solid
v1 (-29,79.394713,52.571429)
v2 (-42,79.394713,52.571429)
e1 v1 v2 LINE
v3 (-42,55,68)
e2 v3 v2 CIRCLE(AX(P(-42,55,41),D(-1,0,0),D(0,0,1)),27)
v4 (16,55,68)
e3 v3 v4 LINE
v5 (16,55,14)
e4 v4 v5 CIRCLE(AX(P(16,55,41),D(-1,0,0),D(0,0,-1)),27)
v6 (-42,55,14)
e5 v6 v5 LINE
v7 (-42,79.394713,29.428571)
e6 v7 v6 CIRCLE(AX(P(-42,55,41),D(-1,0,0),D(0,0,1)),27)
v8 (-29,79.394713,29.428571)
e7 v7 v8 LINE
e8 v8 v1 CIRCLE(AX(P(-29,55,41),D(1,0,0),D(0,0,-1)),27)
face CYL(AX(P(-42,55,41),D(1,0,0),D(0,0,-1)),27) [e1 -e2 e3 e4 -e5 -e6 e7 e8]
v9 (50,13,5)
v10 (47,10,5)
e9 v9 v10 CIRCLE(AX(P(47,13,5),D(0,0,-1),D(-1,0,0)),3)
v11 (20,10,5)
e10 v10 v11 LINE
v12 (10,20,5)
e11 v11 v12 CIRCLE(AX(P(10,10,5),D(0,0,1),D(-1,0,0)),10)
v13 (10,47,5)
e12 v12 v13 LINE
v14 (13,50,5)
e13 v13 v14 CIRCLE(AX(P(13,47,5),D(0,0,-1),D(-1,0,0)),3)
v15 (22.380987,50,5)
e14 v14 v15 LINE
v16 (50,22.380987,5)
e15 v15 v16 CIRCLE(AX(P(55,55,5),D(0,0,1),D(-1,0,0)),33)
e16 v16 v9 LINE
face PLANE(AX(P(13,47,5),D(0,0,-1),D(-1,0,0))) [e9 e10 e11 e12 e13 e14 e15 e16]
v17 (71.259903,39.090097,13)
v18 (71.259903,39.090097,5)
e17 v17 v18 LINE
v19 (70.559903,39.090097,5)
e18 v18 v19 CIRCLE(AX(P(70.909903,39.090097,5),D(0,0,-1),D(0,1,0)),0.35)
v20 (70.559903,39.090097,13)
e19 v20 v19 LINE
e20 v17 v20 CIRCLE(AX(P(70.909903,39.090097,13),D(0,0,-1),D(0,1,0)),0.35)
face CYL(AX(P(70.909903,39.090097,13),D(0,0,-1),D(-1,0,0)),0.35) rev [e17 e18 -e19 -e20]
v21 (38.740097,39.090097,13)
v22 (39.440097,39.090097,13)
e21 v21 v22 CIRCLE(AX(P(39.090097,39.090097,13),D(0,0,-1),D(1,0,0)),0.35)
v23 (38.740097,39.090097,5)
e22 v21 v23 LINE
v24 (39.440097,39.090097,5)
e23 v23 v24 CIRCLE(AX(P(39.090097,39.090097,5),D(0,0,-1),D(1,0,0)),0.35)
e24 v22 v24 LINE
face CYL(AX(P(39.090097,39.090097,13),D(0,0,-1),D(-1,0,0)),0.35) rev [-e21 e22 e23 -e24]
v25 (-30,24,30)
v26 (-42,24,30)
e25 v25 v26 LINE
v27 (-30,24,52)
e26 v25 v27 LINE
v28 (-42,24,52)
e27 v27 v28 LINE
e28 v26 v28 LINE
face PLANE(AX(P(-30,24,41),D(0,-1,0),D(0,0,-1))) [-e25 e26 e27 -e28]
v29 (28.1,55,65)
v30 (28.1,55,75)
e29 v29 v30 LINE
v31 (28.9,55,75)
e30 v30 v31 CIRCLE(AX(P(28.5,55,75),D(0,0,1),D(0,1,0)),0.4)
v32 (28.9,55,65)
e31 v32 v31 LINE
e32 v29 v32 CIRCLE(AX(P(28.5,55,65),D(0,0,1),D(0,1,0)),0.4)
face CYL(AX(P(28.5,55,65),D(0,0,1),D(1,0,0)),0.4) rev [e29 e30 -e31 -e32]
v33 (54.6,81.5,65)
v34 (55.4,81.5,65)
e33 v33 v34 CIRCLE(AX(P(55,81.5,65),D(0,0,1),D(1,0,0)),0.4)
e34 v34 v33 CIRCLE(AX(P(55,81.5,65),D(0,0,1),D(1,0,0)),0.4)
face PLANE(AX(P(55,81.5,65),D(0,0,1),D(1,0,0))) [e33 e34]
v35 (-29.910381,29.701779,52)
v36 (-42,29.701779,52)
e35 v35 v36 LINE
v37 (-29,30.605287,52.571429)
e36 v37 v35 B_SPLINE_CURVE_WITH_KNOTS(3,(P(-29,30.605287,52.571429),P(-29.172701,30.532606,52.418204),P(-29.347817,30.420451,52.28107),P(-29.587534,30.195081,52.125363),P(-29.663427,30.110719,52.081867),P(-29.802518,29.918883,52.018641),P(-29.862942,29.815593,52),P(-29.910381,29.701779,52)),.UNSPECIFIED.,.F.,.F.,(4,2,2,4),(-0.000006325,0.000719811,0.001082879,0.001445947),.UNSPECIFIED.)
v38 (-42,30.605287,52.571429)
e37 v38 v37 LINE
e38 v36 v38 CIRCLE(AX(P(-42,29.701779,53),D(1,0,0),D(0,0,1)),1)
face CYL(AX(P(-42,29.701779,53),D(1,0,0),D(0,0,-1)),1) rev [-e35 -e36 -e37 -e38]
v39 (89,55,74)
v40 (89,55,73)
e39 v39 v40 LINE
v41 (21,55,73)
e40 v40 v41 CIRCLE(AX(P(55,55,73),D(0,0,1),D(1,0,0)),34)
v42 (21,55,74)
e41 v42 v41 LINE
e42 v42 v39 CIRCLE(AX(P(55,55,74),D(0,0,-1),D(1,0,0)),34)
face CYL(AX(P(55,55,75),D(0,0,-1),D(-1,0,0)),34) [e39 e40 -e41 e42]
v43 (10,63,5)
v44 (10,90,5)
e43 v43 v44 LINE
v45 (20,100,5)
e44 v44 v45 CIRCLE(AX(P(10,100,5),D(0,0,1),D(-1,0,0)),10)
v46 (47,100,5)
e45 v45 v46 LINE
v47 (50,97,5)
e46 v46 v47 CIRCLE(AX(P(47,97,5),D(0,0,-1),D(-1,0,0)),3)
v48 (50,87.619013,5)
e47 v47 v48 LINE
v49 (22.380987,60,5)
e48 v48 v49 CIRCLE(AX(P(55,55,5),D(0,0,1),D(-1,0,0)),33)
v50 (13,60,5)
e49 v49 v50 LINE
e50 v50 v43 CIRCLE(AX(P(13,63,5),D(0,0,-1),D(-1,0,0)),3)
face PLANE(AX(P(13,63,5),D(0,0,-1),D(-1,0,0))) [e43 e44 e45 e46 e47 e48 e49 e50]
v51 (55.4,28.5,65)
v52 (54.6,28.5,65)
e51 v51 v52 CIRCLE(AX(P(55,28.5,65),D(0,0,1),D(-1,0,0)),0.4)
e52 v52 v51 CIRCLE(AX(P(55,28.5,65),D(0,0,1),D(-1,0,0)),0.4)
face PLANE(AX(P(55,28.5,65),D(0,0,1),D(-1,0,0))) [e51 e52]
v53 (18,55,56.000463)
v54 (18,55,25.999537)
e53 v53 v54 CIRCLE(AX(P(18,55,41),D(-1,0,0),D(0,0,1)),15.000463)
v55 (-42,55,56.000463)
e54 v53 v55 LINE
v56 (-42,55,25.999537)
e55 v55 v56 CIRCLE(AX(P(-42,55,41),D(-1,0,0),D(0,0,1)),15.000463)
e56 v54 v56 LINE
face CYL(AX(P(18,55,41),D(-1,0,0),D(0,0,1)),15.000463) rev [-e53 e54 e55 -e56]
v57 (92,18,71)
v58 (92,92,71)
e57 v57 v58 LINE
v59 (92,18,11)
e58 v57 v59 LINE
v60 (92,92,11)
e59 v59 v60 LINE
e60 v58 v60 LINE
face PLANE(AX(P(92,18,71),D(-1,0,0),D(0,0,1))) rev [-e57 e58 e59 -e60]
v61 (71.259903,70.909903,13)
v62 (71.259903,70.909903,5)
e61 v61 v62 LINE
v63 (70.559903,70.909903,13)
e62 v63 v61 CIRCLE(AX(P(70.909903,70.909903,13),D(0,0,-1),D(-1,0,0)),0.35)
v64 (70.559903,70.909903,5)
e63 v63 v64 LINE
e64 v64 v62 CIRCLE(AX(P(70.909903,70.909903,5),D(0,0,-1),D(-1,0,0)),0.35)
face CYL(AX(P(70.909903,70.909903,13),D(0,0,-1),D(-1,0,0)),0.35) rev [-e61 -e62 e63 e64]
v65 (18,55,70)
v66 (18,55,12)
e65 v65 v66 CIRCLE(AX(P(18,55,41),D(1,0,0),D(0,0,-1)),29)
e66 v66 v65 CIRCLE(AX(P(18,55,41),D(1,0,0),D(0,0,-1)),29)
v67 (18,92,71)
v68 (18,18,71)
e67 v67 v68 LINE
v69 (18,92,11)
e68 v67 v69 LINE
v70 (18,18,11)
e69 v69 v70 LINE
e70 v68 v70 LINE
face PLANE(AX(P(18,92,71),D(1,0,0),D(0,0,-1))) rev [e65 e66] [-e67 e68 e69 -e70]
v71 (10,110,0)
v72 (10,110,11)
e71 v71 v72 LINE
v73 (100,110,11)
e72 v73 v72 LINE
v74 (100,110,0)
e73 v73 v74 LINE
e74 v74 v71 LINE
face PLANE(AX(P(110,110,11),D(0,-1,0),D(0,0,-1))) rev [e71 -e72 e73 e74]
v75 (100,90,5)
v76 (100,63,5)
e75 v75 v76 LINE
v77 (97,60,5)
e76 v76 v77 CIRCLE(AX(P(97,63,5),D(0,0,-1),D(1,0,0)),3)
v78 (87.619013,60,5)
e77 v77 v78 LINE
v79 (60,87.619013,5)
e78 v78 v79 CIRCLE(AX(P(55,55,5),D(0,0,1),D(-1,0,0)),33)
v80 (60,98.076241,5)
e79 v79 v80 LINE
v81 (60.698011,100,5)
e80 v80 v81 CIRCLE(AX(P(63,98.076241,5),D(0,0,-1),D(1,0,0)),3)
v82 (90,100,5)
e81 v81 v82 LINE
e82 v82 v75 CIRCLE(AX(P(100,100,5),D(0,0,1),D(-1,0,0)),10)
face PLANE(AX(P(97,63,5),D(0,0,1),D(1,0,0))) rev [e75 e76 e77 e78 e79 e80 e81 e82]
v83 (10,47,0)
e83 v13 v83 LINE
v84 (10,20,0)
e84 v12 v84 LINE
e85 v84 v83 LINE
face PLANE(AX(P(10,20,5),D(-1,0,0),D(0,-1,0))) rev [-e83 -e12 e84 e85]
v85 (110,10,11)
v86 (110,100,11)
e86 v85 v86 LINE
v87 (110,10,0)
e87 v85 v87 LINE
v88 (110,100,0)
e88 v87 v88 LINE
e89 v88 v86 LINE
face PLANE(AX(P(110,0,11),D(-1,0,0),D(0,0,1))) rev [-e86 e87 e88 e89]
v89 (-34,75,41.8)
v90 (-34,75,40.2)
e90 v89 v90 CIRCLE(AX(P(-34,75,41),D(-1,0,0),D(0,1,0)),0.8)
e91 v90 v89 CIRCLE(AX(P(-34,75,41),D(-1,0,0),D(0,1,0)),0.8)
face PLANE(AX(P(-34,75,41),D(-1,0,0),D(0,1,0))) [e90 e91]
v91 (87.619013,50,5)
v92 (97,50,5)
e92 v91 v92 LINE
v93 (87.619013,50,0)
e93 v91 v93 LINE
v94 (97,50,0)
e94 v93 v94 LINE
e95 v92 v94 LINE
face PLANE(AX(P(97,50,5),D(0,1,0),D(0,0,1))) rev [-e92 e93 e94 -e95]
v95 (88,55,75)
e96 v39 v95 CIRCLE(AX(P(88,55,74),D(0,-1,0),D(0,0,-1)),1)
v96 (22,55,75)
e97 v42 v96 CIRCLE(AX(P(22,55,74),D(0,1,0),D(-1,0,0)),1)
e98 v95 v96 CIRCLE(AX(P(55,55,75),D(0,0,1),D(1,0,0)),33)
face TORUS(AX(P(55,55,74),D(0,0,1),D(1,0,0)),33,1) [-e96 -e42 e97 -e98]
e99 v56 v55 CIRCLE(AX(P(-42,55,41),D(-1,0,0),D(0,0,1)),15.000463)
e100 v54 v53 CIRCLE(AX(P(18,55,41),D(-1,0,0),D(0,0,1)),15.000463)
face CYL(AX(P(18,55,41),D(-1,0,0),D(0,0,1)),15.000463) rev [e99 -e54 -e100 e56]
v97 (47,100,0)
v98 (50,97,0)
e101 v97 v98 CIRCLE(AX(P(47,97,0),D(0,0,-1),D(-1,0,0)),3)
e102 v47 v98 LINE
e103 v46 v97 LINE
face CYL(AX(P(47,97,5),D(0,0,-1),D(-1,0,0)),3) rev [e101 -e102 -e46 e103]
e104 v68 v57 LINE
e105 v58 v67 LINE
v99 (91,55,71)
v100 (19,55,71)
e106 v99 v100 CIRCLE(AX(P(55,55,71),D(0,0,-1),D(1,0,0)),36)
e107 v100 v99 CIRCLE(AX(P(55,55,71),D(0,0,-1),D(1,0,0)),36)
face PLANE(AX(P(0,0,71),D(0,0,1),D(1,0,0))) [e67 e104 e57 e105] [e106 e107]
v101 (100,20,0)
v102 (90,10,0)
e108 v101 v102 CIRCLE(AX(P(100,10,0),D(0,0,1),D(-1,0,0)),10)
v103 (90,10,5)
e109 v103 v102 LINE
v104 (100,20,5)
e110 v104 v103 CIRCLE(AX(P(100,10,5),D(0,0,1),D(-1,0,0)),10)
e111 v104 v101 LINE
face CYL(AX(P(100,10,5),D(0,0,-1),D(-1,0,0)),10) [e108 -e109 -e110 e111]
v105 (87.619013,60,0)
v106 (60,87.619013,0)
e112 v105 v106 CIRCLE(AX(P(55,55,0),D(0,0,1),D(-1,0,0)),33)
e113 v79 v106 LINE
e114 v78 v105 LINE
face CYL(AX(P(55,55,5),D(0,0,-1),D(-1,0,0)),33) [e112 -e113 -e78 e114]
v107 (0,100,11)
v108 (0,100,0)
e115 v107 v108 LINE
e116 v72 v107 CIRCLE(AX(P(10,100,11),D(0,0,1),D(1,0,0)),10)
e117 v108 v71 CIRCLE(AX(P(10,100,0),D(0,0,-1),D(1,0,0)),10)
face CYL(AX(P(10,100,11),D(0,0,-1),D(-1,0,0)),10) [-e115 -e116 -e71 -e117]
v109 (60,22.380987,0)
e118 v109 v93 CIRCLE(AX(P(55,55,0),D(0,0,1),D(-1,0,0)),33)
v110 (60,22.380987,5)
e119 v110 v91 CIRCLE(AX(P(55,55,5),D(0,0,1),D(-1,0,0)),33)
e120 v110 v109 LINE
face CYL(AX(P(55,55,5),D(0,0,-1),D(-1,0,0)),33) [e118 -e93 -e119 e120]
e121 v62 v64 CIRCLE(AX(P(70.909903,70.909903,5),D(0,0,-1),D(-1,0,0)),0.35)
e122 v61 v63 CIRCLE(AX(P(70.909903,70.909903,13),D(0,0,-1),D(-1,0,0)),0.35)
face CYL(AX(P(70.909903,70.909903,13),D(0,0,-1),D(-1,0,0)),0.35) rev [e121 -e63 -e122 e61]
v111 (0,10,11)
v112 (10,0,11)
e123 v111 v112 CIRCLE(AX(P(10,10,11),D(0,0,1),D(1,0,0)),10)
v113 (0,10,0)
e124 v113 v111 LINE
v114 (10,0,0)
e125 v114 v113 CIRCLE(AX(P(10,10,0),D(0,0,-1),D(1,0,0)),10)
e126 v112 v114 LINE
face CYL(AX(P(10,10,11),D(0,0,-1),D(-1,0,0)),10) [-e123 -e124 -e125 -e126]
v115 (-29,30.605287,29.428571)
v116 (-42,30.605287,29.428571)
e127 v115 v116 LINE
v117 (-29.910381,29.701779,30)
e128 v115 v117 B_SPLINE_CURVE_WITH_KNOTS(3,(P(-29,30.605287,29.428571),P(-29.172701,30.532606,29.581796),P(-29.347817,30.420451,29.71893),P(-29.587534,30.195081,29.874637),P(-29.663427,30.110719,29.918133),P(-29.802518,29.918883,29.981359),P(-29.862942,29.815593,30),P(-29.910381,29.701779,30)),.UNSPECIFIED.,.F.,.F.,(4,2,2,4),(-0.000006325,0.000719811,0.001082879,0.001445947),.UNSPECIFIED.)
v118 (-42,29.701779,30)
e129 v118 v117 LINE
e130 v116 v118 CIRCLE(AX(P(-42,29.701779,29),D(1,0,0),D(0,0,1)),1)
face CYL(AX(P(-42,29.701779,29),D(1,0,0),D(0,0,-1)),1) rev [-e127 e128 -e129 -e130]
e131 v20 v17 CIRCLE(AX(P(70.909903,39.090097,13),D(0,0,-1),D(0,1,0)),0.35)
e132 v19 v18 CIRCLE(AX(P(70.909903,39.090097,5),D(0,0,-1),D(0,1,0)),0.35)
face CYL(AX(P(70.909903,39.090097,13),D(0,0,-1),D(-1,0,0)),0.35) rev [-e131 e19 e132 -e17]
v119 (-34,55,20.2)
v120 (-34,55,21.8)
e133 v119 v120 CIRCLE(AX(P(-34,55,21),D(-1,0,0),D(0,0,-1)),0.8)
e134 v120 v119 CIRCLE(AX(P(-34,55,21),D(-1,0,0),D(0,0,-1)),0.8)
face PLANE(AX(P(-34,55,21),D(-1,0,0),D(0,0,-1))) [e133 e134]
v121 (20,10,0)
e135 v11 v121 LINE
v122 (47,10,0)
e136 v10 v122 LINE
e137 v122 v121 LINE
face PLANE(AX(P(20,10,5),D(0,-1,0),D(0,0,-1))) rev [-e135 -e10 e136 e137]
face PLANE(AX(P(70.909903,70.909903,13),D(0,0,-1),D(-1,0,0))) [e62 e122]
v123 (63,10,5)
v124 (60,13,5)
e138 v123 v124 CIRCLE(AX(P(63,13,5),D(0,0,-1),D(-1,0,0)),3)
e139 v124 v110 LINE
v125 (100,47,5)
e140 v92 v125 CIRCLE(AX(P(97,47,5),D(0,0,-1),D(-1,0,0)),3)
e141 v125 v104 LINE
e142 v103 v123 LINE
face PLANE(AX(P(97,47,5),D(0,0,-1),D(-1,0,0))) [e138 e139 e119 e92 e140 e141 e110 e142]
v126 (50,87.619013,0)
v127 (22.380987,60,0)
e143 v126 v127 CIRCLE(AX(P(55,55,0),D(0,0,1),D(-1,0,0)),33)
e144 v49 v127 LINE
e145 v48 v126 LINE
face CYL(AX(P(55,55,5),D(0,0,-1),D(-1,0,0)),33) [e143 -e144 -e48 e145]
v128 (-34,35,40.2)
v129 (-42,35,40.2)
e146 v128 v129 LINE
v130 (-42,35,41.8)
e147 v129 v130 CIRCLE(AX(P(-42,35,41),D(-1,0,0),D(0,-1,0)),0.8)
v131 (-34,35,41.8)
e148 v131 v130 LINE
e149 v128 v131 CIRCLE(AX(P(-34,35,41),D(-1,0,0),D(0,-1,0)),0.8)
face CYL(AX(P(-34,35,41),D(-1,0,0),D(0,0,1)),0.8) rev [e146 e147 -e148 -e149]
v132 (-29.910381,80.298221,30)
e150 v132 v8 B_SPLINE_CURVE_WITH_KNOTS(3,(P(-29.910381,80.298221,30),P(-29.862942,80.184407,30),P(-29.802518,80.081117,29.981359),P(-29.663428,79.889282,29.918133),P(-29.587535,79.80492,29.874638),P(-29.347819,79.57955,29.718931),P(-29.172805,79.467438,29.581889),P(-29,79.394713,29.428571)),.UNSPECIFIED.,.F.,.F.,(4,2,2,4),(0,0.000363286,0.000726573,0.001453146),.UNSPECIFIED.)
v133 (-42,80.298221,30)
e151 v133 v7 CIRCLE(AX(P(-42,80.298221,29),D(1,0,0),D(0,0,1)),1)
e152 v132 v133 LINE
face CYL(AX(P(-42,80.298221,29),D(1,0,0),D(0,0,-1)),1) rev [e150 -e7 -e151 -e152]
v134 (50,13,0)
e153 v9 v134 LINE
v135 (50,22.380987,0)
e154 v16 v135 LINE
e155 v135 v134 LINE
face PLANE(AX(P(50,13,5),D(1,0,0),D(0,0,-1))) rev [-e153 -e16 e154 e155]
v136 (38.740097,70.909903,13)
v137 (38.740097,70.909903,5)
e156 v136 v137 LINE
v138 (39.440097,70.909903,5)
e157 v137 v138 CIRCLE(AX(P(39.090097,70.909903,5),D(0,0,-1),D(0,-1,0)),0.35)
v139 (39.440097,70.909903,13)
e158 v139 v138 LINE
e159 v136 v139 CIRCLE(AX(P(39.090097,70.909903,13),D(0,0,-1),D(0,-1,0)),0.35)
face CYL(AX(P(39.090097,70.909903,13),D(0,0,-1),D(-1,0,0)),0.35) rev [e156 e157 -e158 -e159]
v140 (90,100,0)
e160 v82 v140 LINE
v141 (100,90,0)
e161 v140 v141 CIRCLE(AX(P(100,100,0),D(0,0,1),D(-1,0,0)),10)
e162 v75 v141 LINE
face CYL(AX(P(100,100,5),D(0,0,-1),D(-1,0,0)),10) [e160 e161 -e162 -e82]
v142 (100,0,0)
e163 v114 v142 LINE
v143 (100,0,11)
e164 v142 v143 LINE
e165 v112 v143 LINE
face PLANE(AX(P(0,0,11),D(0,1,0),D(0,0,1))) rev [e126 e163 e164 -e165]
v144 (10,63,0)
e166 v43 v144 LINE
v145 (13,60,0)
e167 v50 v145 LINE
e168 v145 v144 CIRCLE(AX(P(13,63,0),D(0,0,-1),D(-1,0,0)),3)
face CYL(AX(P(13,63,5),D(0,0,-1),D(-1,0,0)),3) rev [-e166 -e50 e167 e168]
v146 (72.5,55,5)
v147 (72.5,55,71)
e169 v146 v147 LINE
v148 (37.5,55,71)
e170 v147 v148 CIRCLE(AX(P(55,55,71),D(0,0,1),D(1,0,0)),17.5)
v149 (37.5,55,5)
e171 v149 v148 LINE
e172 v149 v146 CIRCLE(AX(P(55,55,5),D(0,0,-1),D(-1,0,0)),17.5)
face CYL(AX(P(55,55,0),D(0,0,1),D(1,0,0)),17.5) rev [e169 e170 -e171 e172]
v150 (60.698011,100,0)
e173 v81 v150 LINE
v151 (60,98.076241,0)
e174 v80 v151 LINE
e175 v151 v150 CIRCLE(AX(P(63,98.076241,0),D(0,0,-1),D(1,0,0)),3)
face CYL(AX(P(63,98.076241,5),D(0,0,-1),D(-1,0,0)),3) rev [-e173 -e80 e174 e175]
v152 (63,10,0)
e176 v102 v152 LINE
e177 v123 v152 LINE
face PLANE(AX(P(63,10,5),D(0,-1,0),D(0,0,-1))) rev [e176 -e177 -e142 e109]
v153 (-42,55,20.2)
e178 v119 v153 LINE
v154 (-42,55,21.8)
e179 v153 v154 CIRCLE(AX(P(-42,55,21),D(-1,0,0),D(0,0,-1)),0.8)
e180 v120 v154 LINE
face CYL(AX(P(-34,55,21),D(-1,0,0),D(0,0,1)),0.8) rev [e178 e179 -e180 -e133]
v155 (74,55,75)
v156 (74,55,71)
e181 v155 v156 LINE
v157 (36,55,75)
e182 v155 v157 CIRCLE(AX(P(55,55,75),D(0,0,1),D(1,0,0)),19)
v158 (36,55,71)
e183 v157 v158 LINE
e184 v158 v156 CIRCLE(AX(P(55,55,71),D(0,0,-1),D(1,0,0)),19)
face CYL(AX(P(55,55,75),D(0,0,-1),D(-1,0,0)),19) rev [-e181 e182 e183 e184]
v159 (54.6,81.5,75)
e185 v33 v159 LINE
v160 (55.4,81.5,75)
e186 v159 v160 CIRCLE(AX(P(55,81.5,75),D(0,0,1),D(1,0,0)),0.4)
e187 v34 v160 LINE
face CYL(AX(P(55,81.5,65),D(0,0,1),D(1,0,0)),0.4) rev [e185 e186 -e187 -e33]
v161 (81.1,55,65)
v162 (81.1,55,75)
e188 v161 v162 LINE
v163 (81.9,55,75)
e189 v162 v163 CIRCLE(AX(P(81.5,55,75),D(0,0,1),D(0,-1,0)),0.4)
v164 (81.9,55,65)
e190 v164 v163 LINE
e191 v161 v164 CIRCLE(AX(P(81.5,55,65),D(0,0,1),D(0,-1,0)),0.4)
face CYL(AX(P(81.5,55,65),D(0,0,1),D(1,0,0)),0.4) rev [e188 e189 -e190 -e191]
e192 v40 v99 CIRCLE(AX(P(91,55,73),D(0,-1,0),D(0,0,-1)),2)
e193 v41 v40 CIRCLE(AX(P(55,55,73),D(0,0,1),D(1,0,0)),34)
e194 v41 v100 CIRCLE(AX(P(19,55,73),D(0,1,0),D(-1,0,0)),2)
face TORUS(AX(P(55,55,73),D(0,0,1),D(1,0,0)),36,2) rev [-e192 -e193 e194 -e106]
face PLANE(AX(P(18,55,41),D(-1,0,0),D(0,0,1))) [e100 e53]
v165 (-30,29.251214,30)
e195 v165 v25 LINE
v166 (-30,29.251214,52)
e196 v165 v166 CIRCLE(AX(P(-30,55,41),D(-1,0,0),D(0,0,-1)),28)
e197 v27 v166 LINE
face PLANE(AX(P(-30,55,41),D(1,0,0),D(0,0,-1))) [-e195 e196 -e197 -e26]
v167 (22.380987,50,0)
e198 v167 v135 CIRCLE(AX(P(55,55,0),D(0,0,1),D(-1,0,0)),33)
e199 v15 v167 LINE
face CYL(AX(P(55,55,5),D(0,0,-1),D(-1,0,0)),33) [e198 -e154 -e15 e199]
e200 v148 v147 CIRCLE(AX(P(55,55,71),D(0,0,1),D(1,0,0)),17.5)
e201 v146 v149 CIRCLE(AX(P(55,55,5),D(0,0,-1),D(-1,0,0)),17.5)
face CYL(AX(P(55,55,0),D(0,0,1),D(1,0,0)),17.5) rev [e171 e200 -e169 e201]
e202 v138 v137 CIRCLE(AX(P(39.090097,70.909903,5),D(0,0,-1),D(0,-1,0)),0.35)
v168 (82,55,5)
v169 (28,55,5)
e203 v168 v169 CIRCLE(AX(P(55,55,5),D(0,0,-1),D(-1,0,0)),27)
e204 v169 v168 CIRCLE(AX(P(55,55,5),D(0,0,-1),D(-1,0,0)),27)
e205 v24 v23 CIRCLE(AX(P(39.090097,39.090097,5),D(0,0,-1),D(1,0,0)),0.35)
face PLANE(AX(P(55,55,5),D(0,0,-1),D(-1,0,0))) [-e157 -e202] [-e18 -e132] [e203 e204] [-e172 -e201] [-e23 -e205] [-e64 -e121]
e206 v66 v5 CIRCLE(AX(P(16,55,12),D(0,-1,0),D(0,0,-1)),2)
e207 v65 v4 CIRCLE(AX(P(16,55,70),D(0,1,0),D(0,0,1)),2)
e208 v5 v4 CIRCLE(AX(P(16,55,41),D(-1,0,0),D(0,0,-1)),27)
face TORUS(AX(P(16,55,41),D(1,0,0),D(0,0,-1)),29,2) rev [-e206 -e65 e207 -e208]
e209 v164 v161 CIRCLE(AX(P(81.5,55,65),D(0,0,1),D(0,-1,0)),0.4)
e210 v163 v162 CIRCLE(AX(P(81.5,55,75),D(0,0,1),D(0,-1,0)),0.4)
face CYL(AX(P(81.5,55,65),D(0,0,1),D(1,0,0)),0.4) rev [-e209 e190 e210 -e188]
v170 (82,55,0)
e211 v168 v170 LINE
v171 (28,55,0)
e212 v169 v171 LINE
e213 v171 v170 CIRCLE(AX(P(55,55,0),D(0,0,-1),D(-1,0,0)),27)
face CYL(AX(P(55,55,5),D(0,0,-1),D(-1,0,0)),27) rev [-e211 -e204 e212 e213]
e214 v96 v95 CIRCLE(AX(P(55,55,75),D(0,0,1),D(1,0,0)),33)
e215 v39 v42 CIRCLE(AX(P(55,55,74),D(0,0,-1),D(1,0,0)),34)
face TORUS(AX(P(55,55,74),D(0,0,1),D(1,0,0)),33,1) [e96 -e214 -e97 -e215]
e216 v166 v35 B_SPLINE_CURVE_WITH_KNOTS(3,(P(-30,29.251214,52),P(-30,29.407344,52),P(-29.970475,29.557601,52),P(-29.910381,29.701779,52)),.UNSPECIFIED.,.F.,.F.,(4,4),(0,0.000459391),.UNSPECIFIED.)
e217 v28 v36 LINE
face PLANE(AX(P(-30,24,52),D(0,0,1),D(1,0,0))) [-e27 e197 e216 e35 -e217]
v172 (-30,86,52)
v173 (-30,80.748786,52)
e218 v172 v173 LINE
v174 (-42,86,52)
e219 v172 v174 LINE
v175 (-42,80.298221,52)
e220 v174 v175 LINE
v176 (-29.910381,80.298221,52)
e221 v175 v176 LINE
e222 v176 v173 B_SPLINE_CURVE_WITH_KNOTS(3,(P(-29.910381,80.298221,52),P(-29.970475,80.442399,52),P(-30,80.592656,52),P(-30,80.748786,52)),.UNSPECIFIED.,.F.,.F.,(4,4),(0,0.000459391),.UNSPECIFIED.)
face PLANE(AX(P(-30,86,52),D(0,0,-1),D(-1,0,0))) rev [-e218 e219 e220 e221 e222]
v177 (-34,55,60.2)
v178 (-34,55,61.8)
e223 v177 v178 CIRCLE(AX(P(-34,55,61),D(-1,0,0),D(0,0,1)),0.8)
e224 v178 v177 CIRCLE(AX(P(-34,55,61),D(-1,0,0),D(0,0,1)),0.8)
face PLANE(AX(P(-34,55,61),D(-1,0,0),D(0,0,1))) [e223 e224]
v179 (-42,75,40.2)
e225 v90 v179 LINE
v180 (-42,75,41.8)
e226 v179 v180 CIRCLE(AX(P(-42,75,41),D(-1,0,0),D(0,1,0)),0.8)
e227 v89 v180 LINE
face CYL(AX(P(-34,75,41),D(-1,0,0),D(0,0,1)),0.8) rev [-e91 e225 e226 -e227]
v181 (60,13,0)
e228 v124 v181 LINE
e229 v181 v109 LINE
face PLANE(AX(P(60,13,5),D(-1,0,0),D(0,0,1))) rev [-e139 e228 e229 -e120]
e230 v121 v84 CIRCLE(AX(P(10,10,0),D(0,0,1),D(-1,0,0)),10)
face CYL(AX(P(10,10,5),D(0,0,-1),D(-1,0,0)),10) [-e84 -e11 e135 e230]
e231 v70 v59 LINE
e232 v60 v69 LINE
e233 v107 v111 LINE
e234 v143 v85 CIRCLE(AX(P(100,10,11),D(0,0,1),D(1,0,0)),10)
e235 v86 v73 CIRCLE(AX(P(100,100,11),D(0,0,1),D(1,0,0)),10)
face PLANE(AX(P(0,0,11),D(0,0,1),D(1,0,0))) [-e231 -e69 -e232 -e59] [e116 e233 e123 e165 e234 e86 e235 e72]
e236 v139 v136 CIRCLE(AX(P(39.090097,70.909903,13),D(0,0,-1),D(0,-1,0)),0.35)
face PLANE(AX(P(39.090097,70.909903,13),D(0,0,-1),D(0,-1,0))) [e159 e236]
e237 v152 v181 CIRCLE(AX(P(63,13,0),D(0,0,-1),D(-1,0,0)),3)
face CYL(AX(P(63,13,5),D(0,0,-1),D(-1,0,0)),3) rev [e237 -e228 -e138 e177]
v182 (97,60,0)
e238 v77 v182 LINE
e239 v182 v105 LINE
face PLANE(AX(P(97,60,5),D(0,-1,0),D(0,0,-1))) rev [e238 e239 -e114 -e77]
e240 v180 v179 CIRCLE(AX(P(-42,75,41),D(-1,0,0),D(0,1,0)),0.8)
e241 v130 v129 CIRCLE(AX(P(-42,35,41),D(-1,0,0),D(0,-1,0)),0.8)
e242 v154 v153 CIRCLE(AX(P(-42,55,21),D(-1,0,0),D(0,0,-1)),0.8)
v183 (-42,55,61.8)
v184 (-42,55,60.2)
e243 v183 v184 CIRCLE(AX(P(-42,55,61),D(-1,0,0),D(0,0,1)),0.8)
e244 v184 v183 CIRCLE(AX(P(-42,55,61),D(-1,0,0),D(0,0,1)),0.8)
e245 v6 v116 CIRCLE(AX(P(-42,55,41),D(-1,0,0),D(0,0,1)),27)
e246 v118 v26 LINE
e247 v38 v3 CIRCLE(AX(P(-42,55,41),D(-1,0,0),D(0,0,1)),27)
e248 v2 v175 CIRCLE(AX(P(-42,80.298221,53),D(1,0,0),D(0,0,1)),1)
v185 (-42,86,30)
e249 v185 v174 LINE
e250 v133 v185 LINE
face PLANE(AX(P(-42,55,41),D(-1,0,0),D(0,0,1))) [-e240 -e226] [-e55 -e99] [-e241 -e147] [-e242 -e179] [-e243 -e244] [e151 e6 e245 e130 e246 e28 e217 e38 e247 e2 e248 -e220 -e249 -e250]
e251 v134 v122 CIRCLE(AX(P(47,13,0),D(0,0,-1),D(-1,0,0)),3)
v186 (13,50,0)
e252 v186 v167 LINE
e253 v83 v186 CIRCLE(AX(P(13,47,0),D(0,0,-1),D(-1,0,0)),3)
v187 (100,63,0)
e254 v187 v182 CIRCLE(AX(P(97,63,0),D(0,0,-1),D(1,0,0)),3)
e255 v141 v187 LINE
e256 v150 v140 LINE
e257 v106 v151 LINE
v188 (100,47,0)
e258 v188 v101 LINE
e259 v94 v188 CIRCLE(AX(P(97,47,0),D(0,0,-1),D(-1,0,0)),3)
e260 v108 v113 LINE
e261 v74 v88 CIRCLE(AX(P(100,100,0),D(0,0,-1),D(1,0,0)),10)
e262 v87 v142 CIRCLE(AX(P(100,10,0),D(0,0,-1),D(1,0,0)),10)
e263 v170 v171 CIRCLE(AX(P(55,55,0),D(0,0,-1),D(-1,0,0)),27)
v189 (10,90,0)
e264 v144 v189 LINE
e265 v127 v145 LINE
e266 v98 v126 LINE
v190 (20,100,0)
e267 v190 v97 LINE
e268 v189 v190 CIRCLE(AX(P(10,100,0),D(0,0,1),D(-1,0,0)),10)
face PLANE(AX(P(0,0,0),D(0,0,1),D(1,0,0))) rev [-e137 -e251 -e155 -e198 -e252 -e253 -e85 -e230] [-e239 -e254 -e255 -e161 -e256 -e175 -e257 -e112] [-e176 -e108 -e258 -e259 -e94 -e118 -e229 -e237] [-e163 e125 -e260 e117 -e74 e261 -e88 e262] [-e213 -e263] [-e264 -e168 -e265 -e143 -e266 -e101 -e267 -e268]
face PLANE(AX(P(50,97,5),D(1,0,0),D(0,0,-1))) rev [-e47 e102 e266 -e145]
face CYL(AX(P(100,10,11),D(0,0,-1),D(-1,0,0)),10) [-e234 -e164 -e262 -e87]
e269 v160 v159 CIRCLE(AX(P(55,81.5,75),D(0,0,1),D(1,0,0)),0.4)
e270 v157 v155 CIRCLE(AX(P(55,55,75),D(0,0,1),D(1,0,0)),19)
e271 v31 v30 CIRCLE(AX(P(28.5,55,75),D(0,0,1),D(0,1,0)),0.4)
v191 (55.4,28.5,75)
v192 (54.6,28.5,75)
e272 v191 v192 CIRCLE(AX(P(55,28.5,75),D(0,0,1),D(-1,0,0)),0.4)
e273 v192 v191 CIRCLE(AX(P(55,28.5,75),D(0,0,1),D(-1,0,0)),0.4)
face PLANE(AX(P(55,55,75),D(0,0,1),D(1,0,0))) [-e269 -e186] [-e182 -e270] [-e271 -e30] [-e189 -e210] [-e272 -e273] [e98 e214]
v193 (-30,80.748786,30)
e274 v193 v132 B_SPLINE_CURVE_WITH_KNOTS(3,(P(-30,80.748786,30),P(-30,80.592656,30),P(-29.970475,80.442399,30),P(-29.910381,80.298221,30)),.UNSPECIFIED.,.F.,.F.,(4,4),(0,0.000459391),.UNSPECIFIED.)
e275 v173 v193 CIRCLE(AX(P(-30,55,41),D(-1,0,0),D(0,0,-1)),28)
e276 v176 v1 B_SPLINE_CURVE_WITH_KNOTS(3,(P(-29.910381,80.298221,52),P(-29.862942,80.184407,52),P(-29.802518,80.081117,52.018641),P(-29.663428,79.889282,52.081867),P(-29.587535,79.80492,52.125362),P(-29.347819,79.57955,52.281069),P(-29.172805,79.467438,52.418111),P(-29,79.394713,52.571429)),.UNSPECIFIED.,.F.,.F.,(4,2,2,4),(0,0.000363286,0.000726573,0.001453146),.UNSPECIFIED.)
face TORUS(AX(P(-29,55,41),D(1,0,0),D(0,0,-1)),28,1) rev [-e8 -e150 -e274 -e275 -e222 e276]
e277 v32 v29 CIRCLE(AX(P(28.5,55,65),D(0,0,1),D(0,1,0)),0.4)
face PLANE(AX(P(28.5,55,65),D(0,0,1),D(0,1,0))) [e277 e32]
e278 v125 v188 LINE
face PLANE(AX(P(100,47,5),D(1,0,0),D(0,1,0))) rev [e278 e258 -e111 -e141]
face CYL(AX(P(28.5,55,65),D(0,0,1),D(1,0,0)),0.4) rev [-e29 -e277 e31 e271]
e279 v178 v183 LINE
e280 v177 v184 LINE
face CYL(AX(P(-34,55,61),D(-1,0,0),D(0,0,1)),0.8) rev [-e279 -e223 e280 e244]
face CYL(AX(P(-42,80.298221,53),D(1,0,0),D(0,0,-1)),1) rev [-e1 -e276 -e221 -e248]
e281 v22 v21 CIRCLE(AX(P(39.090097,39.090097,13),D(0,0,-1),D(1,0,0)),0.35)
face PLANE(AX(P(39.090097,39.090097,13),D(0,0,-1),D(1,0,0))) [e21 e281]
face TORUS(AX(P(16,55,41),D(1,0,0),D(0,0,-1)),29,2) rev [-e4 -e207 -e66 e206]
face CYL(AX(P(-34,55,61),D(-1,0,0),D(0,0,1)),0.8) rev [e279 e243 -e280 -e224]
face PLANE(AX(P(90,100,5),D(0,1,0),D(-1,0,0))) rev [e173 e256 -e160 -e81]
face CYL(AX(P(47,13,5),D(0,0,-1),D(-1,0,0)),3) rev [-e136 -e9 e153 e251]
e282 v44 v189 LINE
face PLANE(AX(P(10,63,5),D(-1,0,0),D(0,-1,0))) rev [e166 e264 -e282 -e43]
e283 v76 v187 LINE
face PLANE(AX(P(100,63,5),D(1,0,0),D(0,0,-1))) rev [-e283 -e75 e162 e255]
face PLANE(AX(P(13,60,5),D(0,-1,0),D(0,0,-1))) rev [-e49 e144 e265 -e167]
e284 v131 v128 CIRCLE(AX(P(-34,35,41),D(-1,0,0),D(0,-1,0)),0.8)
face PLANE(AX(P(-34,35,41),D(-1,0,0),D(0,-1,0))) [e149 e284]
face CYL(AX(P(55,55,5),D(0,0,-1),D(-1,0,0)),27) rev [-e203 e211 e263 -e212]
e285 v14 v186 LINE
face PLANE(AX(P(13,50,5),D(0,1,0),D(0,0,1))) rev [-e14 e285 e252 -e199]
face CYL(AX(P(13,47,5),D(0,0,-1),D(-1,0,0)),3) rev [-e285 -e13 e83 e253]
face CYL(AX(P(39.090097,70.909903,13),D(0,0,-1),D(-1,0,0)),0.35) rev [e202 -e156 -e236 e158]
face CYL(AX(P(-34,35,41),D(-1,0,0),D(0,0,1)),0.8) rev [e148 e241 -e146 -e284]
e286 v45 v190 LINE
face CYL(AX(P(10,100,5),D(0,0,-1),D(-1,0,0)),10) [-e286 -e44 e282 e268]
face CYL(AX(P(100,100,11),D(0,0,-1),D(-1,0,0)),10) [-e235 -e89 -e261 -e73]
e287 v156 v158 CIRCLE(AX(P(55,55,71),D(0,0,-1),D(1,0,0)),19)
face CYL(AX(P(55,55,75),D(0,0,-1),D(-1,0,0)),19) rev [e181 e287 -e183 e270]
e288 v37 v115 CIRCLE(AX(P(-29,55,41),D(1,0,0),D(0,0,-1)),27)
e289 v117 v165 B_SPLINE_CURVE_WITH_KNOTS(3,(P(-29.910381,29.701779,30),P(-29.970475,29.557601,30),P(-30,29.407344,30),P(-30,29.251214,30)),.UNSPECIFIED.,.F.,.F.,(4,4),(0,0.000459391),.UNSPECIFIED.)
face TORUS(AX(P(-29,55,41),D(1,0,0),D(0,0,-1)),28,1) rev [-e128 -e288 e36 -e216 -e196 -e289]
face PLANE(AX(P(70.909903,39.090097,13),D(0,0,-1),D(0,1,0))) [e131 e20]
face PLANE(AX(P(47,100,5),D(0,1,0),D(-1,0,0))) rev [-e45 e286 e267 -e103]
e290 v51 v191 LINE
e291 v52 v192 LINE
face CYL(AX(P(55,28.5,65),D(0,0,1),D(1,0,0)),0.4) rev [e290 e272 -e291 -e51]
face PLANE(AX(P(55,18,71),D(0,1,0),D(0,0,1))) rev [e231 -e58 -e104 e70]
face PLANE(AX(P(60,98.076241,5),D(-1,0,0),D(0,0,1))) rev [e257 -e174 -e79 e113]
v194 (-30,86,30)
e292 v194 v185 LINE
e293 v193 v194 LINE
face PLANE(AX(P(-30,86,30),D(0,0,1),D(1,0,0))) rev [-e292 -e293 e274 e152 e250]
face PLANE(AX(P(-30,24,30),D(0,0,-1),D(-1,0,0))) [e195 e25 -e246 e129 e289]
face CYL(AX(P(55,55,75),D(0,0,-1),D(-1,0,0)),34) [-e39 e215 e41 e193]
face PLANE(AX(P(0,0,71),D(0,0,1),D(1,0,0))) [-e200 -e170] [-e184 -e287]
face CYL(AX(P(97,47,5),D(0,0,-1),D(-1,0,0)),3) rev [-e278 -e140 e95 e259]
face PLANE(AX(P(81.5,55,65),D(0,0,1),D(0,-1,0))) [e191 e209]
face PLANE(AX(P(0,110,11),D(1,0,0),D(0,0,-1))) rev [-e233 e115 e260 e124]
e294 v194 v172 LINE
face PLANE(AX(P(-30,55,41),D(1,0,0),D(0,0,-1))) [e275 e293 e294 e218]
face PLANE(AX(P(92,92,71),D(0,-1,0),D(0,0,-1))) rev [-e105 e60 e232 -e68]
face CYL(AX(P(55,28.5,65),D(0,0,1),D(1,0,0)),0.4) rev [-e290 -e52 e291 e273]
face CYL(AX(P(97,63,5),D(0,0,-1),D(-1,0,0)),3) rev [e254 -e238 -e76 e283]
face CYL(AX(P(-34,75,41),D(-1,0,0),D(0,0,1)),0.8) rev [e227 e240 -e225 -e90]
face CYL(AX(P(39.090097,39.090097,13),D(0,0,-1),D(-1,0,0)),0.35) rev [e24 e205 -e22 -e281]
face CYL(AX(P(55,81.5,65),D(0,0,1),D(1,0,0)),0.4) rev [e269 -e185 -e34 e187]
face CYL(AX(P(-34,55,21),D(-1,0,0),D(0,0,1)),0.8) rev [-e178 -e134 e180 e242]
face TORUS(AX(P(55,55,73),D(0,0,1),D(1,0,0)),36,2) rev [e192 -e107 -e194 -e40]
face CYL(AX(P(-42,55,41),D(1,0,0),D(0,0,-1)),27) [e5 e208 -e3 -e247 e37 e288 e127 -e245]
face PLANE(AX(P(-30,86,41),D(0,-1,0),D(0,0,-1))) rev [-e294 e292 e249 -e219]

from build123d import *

# Parameters (mm, degrees)
MOUNTING_FLANGE_SKETCH_W      = 110
MOUNTING_FLANGE_SKETCH_H      = 110
MOUNTING_FLANGE_110X110_DEPTH = 11
FLANGE_RECESS_SKETCH_R        = 27
FLANGE_RECESS_SKETCH_R_2      = 17.5
FLANGE_RECESS_DEPTH           = 5
BODY_BLOCK_74X74_DEPTH        = 60
NECK_SKETCH_R                 = 27
CYLINDRICAL_NECK_54_DEPTH     = 60
NECK_START                    = 12
NECK_KEY_LUG_DEPTH            = 12
NECK_BORE_SKETCH_R            = 15.000462615
NECK_BORE_30_DEPTH            = 60
NECK_MARK_SKETCH_R            = 0.8
NECK_MARK_DEPTH               = 8
NECK_MARK_PATTERN_4X_COUNT    = 4
FRONT_COLLAR_SKETCH_R         = 34
FRONT_COLLAR_SKETCH_R_2       = 19
FRONT_COLLAR_RING_68_DEPTH    = 4
FRONT_BORE_SKETCH_R           = 17.5
FRONT_BORE_35_DEPTH           = 172
COLLAR_MARK_SKETCH_R          = 0.4
COLLAR_MARK_DEPTH             = 10
COLLAR_MARK_PATTERN_4X_COUNT  = 4
RECESS_MARK_SKETCH_R          = 0.35
RECESS_MARK_DEPTH             = 8
RECESS_MARK_PATTERN_4X_COUNT  = 4
FLANGE_CORNER_FILLETS_R10_R   = 10
COLLAR_EDGE_FILLET_R1_R       = 1
COLLAR_ROOT_FILLET_R2_R       = 2
NECK_ROOT_FILLET_R2_R         = 2
KEY_LUG_FILLETS_R1_R          = 1


with BuildPart() as part:
    # Mounting Flange Sketch → Mounting Flange 110x110 (new body)
    with BuildSketch(Plane.XY):
        with Locations((55, 55)):
            Rectangle(MOUNTING_FLANGE_SKETCH_W, MOUNTING_FLANGE_SKETCH_H)
    extrude(amount=MOUNTING_FLANGE_110X110_DEPTH)

    # Flange Recess Sketch → Flange Recess (cut)
    # profile 1 of 5: a face of its own
    with BuildSketch(Plane(origin=(0, 0, 0), x_dir=(-1, 0, 0), z_dir=(0, 0, -1))):
        with Locations((-55, 55)):
            Circle(FLANGE_RECESS_SKETCH_R)
        with Locations((-55, 55)):
            Circle(FLANGE_RECESS_SKETCH_R_2, mode=Mode.SUBTRACT)
    # profile 2 of 5: a face of its own
    with BuildSketch(Plane(origin=(0, 0, 0), x_dir=(-1, 0, 0), z_dir=(0, 0, -1))):
        with BuildLine():
            Line((-50, 13), (-50, 22.380987139))
            ThreePointArc((-50, 22.380987139), (-31.665476221, 31.665476221), (-22.380987139, 50))
            Line((-22.380987139, 50), (-13, 50))
            ThreePointArc((-13, 50), (-10.878679656, 49.121320344), (-10, 47))
            Line((-10, 47), (-10, 20))
            ThreePointArc((-10, 20), (-17.071067812, 17.071067812), (-20, 10))
            Line((-20, 10), (-47, 10))
            ThreePointArc((-47, 10), (-49.121320344, 10.878679656), (-50, 13))
        make_face()
    # profile 3 of 5: a face of its own
    with BuildSketch(Plane(origin=(0, 0, 0), x_dir=(-1, 0, 0), z_dir=(0, 0, -1))):
        with BuildLine():
            Line((-60, 13), (-60, 22.380987139))
            ThreePointArc((-60, 22.380987139), (-78.334523779, 31.665476221), (-87.619012861, 50))
            Line((-87.619012861, 50), (-97, 50))
            ThreePointArc((-97, 50), (-99.121320344, 49.121320344), (-100, 47))
            Line((-100, 47), (-100, 20))
            ThreePointArc((-100, 20), (-92.928932188, 17.071067812), (-90, 10))
            Line((-90, 10), (-63, 10))
            ThreePointArc((-63, 10), (-60.878679656, 10.878679656), (-60, 13))
        make_face()
    # profile 4 of 5: a face of its own
    with BuildSketch(Plane(origin=(0, 0, 0), x_dir=(-1, 0, 0), z_dir=(0, 0, -1))):
        with BuildLine():
            Line((-97, 60), (-87.619012861, 60))
            ThreePointArc((-87.619012861, 60), (-78.334523779, 78.334523779), (-60, 87.619012861))
            Line((-60, 87.619012861), (-60, 98.076241066))
            ThreePointArc((-60, 98.076241066), (-60.179896648, 99.099479593), (-60.698011389, 100))
            Line((-60.698011389, 100), (-90, 100))
            ThreePointArc((-90, 100), (-92.928932188, 92.928932188), (-100, 90))
            Line((-100, 90), (-100, 63))
            ThreePointArc((-100, 63), (-99.121320344, 60.878679656), (-97, 60))
        make_face()
    # profile 5 of 5: a face of its own
    with BuildSketch(Plane(origin=(0, 0, 0), x_dir=(-1, 0, 0), z_dir=(0, 0, -1))):
        with BuildLine():
            Line((-50, 97), (-50, 87.619012861))
            ThreePointArc((-50, 87.619012861), (-31.665476221, 78.334523779), (-22.380987139, 60))
            Line((-22.380987139, 60), (-13, 60))
            ThreePointArc((-13, 60), (-10.878679656, 60.878679656), (-10, 63))
            Line((-10, 63), (-10, 90))
            ThreePointArc((-10, 90), (-17.071067812, 92.928932188), (-20, 100))
            Line((-20, 100), (-47, 100))
            ThreePointArc((-47, 100), (-49.121320344, 99.121320344), (-50, 97))
        make_face()
    extrude(amount=-FLANGE_RECESS_DEPTH, mode=Mode.SUBTRACT)

    # Body Block Sketch → Body Block 74x74 (add)
    with BuildSketch(Plane.XY.offset(11)):
        Polygon((55, 18), (92, 18), (92, 92), (18, 92), (18, 18), align=None)
    extrude(amount=BODY_BLOCK_74X74_DEPTH)

    # Neck Sketch → Cylindrical Neck Ø54 (add)
    with BuildSketch(Plane.ZY.offset(-18)):
        with Locations(Location((41, 55, 0), (0, 0, 180))):
            Circle(NECK_SKETCH_R)
    extrude(amount=CYLINDRICAL_NECK_54_DEPTH)

    # Key Lug Sketch → Neck Key Lug (add)
    with BuildSketch(Plane(origin=(-42, 0, 0), x_dir=(0, 0, -1), z_dir=(1, 0, 0)).offset(NECK_START)):
        with BuildLine():
            Line((-41, 86), (-30, 86))
            Line((-30, 86), (-30, 79.657656012))
            ThreePointArc((-30, 79.657656012), (-41, 82), (-52, 79.657656012))
            Line((-52, 79.657656012), (-52, 86))
            Line((-52, 86), (-41, 86))
        make_face()
    neck_key_lug = extrude(amount=-NECK_KEY_LUG_DEPTH)

    # Key Lug Mirror: Neck Key Lug across plane
    add(neck_key_lug.mirror(Plane.ZX.offset(55)))

    # Neck Bore Sketch → Neck Bore Ø30 (cut)
    with BuildSketch(Plane.ZY.offset(42)):
        with Locations((41, 55)):
            Circle(NECK_BORE_SKETCH_R)
    extrude(amount=-NECK_BORE_30_DEPTH, mode=Mode.SUBTRACT)

    # Neck Mark Sketch → Neck Mark (cut)
    with BuildSketch(Plane.ZY.offset(42)):
        with Locations((61, 55)):
            Circle(NECK_MARK_SKETCH_R)
    neck_mark = extrude(amount=-NECK_MARK_DEPTH, mode=Mode.SUBTRACT)

    # Neck Mark Pattern 4x: Neck Mark ×4 about axis
    neck_mark_pattern_4x_axis = Axis((0, 55, 41), (1, 0, 0))
    for i in range(1, NECK_MARK_PATTERN_4X_COUNT):
        add(neck_mark.rotate(neck_mark_pattern_4x_axis, i * 360 / NECK_MARK_PATTERN_4X_COUNT), mode=Mode.SUBTRACT)

    # Front Collar Sketch → Front Collar Ring Ø68 (add)
    with BuildSketch(Plane.XY.offset(71)):
        with Locations((55, 55)):
            Circle(FRONT_COLLAR_SKETCH_R)
        with Locations((55, 55)):
            Circle(FRONT_COLLAR_SKETCH_R_2, mode=Mode.SUBTRACT)
    extrude(amount=FRONT_COLLAR_RING_68_DEPTH)

    # Front Bore Sketch → Front Bore Ø35 (cut, through all)
    with BuildSketch(Plane.XY.offset(71)):
        with Locations((55, 55)):
            Circle(FRONT_BORE_SKETCH_R)
    extrude(amount=-FRONT_BORE_35_DEPTH, mode=Mode.SUBTRACT)

    # Collar Mark Sketch → Collar Mark (cut)
    with BuildSketch(Plane.XY.offset(75)):
        with Locations((55, 81.5)):
            Circle(COLLAR_MARK_SKETCH_R)
    collar_mark = extrude(amount=-COLLAR_MARK_DEPTH, mode=Mode.SUBTRACT)

    # Collar Mark Pattern 4x: Collar Mark ×4 about axis
    collar_mark_pattern_4x_axis = Axis((55, 55, 0), (0, 0, 1))
    for i in range(1, COLLAR_MARK_PATTERN_4X_COUNT):
        add(collar_mark.rotate(collar_mark_pattern_4x_axis, i * 360 / COLLAR_MARK_PATTERN_4X_COUNT), mode=Mode.SUBTRACT)

    # Recess Mark Sketch → Recess Mark (cut)
    with BuildSketch(Plane(origin=(0, 0, 5), x_dir=(-1, 0, 0), z_dir=(0, 0, -1))):
        with Locations((-70.909902577, 70.909902577)):
            Circle(RECESS_MARK_SKETCH_R)
    recess_mark = extrude(amount=-RECESS_MARK_DEPTH, mode=Mode.SUBTRACT)

    # Recess Mark Pattern 4x: Recess Mark ×4 about axis
    recess_mark_pattern_4x_axis = Axis((55, 55, 0), (0, 0, 1))
    for i in range(1, RECESS_MARK_PATTERN_4X_COUNT):
        add(recess_mark.rotate(recess_mark_pattern_4x_axis, i * 360 / RECESS_MARK_PATTERN_4X_COUNT), mode=Mode.SUBTRACT)

    # Flange Corner Fillets R10
    flange_corner_fillets_r10_edges = [part.edges().sort_by_distance(p)[0] for p in [
        (0, 110, 5.5),
        (110, 110, 5.5),
        (110, 0, 5.5),
        (0, 0, 5.5),
    ]]
    fillet(flange_corner_fillets_r10_edges, radius=FLANGE_CORNER_FILLETS_R10_R)

    # Collar Edge Fillet R1
    collar_edge_fillet_r1_edges = [part.edges().sort_by_distance(p)[0] for p in [
        (21, 55, 75),
    ]]
    fillet(collar_edge_fillet_r1_edges, radius=COLLAR_EDGE_FILLET_R1_R)

    # Collar Root Fillet R2
    collar_root_fillet_r2_edges = [part.edges().sort_by_distance(p)[0] for p in [
        (21, 55, 71),
    ]]
    fillet(collar_root_fillet_r2_edges, radius=COLLAR_ROOT_FILLET_R2_R)

    # Neck Root Fillet R2
    neck_root_fillet_r2_edges = [part.edges().sort_by_distance(p)[0] for p in [
        (18, 55, 68),
    ]]
    fillet(neck_root_fillet_r2_edges, radius=NECK_ROOT_FILLET_R2_R)

    # Key Lug Fillets R1
    key_lug_fillets_r1_edges = [part.edges().sort_by_distance(p)[0] for p in [
        (-36, 79.657656012, 52),
        (-36, 79.657656012, 30),
        (-30, 82, 41),
        (-30, 28, 41),
        (-36, 30.342343988, 30),
        (-36, 30.342343988, 52),
    ]]
    fillet(key_lug_fillets_r1_edges, radius=KEY_LUG_FILLETS_R1_R)


solid = part.part
